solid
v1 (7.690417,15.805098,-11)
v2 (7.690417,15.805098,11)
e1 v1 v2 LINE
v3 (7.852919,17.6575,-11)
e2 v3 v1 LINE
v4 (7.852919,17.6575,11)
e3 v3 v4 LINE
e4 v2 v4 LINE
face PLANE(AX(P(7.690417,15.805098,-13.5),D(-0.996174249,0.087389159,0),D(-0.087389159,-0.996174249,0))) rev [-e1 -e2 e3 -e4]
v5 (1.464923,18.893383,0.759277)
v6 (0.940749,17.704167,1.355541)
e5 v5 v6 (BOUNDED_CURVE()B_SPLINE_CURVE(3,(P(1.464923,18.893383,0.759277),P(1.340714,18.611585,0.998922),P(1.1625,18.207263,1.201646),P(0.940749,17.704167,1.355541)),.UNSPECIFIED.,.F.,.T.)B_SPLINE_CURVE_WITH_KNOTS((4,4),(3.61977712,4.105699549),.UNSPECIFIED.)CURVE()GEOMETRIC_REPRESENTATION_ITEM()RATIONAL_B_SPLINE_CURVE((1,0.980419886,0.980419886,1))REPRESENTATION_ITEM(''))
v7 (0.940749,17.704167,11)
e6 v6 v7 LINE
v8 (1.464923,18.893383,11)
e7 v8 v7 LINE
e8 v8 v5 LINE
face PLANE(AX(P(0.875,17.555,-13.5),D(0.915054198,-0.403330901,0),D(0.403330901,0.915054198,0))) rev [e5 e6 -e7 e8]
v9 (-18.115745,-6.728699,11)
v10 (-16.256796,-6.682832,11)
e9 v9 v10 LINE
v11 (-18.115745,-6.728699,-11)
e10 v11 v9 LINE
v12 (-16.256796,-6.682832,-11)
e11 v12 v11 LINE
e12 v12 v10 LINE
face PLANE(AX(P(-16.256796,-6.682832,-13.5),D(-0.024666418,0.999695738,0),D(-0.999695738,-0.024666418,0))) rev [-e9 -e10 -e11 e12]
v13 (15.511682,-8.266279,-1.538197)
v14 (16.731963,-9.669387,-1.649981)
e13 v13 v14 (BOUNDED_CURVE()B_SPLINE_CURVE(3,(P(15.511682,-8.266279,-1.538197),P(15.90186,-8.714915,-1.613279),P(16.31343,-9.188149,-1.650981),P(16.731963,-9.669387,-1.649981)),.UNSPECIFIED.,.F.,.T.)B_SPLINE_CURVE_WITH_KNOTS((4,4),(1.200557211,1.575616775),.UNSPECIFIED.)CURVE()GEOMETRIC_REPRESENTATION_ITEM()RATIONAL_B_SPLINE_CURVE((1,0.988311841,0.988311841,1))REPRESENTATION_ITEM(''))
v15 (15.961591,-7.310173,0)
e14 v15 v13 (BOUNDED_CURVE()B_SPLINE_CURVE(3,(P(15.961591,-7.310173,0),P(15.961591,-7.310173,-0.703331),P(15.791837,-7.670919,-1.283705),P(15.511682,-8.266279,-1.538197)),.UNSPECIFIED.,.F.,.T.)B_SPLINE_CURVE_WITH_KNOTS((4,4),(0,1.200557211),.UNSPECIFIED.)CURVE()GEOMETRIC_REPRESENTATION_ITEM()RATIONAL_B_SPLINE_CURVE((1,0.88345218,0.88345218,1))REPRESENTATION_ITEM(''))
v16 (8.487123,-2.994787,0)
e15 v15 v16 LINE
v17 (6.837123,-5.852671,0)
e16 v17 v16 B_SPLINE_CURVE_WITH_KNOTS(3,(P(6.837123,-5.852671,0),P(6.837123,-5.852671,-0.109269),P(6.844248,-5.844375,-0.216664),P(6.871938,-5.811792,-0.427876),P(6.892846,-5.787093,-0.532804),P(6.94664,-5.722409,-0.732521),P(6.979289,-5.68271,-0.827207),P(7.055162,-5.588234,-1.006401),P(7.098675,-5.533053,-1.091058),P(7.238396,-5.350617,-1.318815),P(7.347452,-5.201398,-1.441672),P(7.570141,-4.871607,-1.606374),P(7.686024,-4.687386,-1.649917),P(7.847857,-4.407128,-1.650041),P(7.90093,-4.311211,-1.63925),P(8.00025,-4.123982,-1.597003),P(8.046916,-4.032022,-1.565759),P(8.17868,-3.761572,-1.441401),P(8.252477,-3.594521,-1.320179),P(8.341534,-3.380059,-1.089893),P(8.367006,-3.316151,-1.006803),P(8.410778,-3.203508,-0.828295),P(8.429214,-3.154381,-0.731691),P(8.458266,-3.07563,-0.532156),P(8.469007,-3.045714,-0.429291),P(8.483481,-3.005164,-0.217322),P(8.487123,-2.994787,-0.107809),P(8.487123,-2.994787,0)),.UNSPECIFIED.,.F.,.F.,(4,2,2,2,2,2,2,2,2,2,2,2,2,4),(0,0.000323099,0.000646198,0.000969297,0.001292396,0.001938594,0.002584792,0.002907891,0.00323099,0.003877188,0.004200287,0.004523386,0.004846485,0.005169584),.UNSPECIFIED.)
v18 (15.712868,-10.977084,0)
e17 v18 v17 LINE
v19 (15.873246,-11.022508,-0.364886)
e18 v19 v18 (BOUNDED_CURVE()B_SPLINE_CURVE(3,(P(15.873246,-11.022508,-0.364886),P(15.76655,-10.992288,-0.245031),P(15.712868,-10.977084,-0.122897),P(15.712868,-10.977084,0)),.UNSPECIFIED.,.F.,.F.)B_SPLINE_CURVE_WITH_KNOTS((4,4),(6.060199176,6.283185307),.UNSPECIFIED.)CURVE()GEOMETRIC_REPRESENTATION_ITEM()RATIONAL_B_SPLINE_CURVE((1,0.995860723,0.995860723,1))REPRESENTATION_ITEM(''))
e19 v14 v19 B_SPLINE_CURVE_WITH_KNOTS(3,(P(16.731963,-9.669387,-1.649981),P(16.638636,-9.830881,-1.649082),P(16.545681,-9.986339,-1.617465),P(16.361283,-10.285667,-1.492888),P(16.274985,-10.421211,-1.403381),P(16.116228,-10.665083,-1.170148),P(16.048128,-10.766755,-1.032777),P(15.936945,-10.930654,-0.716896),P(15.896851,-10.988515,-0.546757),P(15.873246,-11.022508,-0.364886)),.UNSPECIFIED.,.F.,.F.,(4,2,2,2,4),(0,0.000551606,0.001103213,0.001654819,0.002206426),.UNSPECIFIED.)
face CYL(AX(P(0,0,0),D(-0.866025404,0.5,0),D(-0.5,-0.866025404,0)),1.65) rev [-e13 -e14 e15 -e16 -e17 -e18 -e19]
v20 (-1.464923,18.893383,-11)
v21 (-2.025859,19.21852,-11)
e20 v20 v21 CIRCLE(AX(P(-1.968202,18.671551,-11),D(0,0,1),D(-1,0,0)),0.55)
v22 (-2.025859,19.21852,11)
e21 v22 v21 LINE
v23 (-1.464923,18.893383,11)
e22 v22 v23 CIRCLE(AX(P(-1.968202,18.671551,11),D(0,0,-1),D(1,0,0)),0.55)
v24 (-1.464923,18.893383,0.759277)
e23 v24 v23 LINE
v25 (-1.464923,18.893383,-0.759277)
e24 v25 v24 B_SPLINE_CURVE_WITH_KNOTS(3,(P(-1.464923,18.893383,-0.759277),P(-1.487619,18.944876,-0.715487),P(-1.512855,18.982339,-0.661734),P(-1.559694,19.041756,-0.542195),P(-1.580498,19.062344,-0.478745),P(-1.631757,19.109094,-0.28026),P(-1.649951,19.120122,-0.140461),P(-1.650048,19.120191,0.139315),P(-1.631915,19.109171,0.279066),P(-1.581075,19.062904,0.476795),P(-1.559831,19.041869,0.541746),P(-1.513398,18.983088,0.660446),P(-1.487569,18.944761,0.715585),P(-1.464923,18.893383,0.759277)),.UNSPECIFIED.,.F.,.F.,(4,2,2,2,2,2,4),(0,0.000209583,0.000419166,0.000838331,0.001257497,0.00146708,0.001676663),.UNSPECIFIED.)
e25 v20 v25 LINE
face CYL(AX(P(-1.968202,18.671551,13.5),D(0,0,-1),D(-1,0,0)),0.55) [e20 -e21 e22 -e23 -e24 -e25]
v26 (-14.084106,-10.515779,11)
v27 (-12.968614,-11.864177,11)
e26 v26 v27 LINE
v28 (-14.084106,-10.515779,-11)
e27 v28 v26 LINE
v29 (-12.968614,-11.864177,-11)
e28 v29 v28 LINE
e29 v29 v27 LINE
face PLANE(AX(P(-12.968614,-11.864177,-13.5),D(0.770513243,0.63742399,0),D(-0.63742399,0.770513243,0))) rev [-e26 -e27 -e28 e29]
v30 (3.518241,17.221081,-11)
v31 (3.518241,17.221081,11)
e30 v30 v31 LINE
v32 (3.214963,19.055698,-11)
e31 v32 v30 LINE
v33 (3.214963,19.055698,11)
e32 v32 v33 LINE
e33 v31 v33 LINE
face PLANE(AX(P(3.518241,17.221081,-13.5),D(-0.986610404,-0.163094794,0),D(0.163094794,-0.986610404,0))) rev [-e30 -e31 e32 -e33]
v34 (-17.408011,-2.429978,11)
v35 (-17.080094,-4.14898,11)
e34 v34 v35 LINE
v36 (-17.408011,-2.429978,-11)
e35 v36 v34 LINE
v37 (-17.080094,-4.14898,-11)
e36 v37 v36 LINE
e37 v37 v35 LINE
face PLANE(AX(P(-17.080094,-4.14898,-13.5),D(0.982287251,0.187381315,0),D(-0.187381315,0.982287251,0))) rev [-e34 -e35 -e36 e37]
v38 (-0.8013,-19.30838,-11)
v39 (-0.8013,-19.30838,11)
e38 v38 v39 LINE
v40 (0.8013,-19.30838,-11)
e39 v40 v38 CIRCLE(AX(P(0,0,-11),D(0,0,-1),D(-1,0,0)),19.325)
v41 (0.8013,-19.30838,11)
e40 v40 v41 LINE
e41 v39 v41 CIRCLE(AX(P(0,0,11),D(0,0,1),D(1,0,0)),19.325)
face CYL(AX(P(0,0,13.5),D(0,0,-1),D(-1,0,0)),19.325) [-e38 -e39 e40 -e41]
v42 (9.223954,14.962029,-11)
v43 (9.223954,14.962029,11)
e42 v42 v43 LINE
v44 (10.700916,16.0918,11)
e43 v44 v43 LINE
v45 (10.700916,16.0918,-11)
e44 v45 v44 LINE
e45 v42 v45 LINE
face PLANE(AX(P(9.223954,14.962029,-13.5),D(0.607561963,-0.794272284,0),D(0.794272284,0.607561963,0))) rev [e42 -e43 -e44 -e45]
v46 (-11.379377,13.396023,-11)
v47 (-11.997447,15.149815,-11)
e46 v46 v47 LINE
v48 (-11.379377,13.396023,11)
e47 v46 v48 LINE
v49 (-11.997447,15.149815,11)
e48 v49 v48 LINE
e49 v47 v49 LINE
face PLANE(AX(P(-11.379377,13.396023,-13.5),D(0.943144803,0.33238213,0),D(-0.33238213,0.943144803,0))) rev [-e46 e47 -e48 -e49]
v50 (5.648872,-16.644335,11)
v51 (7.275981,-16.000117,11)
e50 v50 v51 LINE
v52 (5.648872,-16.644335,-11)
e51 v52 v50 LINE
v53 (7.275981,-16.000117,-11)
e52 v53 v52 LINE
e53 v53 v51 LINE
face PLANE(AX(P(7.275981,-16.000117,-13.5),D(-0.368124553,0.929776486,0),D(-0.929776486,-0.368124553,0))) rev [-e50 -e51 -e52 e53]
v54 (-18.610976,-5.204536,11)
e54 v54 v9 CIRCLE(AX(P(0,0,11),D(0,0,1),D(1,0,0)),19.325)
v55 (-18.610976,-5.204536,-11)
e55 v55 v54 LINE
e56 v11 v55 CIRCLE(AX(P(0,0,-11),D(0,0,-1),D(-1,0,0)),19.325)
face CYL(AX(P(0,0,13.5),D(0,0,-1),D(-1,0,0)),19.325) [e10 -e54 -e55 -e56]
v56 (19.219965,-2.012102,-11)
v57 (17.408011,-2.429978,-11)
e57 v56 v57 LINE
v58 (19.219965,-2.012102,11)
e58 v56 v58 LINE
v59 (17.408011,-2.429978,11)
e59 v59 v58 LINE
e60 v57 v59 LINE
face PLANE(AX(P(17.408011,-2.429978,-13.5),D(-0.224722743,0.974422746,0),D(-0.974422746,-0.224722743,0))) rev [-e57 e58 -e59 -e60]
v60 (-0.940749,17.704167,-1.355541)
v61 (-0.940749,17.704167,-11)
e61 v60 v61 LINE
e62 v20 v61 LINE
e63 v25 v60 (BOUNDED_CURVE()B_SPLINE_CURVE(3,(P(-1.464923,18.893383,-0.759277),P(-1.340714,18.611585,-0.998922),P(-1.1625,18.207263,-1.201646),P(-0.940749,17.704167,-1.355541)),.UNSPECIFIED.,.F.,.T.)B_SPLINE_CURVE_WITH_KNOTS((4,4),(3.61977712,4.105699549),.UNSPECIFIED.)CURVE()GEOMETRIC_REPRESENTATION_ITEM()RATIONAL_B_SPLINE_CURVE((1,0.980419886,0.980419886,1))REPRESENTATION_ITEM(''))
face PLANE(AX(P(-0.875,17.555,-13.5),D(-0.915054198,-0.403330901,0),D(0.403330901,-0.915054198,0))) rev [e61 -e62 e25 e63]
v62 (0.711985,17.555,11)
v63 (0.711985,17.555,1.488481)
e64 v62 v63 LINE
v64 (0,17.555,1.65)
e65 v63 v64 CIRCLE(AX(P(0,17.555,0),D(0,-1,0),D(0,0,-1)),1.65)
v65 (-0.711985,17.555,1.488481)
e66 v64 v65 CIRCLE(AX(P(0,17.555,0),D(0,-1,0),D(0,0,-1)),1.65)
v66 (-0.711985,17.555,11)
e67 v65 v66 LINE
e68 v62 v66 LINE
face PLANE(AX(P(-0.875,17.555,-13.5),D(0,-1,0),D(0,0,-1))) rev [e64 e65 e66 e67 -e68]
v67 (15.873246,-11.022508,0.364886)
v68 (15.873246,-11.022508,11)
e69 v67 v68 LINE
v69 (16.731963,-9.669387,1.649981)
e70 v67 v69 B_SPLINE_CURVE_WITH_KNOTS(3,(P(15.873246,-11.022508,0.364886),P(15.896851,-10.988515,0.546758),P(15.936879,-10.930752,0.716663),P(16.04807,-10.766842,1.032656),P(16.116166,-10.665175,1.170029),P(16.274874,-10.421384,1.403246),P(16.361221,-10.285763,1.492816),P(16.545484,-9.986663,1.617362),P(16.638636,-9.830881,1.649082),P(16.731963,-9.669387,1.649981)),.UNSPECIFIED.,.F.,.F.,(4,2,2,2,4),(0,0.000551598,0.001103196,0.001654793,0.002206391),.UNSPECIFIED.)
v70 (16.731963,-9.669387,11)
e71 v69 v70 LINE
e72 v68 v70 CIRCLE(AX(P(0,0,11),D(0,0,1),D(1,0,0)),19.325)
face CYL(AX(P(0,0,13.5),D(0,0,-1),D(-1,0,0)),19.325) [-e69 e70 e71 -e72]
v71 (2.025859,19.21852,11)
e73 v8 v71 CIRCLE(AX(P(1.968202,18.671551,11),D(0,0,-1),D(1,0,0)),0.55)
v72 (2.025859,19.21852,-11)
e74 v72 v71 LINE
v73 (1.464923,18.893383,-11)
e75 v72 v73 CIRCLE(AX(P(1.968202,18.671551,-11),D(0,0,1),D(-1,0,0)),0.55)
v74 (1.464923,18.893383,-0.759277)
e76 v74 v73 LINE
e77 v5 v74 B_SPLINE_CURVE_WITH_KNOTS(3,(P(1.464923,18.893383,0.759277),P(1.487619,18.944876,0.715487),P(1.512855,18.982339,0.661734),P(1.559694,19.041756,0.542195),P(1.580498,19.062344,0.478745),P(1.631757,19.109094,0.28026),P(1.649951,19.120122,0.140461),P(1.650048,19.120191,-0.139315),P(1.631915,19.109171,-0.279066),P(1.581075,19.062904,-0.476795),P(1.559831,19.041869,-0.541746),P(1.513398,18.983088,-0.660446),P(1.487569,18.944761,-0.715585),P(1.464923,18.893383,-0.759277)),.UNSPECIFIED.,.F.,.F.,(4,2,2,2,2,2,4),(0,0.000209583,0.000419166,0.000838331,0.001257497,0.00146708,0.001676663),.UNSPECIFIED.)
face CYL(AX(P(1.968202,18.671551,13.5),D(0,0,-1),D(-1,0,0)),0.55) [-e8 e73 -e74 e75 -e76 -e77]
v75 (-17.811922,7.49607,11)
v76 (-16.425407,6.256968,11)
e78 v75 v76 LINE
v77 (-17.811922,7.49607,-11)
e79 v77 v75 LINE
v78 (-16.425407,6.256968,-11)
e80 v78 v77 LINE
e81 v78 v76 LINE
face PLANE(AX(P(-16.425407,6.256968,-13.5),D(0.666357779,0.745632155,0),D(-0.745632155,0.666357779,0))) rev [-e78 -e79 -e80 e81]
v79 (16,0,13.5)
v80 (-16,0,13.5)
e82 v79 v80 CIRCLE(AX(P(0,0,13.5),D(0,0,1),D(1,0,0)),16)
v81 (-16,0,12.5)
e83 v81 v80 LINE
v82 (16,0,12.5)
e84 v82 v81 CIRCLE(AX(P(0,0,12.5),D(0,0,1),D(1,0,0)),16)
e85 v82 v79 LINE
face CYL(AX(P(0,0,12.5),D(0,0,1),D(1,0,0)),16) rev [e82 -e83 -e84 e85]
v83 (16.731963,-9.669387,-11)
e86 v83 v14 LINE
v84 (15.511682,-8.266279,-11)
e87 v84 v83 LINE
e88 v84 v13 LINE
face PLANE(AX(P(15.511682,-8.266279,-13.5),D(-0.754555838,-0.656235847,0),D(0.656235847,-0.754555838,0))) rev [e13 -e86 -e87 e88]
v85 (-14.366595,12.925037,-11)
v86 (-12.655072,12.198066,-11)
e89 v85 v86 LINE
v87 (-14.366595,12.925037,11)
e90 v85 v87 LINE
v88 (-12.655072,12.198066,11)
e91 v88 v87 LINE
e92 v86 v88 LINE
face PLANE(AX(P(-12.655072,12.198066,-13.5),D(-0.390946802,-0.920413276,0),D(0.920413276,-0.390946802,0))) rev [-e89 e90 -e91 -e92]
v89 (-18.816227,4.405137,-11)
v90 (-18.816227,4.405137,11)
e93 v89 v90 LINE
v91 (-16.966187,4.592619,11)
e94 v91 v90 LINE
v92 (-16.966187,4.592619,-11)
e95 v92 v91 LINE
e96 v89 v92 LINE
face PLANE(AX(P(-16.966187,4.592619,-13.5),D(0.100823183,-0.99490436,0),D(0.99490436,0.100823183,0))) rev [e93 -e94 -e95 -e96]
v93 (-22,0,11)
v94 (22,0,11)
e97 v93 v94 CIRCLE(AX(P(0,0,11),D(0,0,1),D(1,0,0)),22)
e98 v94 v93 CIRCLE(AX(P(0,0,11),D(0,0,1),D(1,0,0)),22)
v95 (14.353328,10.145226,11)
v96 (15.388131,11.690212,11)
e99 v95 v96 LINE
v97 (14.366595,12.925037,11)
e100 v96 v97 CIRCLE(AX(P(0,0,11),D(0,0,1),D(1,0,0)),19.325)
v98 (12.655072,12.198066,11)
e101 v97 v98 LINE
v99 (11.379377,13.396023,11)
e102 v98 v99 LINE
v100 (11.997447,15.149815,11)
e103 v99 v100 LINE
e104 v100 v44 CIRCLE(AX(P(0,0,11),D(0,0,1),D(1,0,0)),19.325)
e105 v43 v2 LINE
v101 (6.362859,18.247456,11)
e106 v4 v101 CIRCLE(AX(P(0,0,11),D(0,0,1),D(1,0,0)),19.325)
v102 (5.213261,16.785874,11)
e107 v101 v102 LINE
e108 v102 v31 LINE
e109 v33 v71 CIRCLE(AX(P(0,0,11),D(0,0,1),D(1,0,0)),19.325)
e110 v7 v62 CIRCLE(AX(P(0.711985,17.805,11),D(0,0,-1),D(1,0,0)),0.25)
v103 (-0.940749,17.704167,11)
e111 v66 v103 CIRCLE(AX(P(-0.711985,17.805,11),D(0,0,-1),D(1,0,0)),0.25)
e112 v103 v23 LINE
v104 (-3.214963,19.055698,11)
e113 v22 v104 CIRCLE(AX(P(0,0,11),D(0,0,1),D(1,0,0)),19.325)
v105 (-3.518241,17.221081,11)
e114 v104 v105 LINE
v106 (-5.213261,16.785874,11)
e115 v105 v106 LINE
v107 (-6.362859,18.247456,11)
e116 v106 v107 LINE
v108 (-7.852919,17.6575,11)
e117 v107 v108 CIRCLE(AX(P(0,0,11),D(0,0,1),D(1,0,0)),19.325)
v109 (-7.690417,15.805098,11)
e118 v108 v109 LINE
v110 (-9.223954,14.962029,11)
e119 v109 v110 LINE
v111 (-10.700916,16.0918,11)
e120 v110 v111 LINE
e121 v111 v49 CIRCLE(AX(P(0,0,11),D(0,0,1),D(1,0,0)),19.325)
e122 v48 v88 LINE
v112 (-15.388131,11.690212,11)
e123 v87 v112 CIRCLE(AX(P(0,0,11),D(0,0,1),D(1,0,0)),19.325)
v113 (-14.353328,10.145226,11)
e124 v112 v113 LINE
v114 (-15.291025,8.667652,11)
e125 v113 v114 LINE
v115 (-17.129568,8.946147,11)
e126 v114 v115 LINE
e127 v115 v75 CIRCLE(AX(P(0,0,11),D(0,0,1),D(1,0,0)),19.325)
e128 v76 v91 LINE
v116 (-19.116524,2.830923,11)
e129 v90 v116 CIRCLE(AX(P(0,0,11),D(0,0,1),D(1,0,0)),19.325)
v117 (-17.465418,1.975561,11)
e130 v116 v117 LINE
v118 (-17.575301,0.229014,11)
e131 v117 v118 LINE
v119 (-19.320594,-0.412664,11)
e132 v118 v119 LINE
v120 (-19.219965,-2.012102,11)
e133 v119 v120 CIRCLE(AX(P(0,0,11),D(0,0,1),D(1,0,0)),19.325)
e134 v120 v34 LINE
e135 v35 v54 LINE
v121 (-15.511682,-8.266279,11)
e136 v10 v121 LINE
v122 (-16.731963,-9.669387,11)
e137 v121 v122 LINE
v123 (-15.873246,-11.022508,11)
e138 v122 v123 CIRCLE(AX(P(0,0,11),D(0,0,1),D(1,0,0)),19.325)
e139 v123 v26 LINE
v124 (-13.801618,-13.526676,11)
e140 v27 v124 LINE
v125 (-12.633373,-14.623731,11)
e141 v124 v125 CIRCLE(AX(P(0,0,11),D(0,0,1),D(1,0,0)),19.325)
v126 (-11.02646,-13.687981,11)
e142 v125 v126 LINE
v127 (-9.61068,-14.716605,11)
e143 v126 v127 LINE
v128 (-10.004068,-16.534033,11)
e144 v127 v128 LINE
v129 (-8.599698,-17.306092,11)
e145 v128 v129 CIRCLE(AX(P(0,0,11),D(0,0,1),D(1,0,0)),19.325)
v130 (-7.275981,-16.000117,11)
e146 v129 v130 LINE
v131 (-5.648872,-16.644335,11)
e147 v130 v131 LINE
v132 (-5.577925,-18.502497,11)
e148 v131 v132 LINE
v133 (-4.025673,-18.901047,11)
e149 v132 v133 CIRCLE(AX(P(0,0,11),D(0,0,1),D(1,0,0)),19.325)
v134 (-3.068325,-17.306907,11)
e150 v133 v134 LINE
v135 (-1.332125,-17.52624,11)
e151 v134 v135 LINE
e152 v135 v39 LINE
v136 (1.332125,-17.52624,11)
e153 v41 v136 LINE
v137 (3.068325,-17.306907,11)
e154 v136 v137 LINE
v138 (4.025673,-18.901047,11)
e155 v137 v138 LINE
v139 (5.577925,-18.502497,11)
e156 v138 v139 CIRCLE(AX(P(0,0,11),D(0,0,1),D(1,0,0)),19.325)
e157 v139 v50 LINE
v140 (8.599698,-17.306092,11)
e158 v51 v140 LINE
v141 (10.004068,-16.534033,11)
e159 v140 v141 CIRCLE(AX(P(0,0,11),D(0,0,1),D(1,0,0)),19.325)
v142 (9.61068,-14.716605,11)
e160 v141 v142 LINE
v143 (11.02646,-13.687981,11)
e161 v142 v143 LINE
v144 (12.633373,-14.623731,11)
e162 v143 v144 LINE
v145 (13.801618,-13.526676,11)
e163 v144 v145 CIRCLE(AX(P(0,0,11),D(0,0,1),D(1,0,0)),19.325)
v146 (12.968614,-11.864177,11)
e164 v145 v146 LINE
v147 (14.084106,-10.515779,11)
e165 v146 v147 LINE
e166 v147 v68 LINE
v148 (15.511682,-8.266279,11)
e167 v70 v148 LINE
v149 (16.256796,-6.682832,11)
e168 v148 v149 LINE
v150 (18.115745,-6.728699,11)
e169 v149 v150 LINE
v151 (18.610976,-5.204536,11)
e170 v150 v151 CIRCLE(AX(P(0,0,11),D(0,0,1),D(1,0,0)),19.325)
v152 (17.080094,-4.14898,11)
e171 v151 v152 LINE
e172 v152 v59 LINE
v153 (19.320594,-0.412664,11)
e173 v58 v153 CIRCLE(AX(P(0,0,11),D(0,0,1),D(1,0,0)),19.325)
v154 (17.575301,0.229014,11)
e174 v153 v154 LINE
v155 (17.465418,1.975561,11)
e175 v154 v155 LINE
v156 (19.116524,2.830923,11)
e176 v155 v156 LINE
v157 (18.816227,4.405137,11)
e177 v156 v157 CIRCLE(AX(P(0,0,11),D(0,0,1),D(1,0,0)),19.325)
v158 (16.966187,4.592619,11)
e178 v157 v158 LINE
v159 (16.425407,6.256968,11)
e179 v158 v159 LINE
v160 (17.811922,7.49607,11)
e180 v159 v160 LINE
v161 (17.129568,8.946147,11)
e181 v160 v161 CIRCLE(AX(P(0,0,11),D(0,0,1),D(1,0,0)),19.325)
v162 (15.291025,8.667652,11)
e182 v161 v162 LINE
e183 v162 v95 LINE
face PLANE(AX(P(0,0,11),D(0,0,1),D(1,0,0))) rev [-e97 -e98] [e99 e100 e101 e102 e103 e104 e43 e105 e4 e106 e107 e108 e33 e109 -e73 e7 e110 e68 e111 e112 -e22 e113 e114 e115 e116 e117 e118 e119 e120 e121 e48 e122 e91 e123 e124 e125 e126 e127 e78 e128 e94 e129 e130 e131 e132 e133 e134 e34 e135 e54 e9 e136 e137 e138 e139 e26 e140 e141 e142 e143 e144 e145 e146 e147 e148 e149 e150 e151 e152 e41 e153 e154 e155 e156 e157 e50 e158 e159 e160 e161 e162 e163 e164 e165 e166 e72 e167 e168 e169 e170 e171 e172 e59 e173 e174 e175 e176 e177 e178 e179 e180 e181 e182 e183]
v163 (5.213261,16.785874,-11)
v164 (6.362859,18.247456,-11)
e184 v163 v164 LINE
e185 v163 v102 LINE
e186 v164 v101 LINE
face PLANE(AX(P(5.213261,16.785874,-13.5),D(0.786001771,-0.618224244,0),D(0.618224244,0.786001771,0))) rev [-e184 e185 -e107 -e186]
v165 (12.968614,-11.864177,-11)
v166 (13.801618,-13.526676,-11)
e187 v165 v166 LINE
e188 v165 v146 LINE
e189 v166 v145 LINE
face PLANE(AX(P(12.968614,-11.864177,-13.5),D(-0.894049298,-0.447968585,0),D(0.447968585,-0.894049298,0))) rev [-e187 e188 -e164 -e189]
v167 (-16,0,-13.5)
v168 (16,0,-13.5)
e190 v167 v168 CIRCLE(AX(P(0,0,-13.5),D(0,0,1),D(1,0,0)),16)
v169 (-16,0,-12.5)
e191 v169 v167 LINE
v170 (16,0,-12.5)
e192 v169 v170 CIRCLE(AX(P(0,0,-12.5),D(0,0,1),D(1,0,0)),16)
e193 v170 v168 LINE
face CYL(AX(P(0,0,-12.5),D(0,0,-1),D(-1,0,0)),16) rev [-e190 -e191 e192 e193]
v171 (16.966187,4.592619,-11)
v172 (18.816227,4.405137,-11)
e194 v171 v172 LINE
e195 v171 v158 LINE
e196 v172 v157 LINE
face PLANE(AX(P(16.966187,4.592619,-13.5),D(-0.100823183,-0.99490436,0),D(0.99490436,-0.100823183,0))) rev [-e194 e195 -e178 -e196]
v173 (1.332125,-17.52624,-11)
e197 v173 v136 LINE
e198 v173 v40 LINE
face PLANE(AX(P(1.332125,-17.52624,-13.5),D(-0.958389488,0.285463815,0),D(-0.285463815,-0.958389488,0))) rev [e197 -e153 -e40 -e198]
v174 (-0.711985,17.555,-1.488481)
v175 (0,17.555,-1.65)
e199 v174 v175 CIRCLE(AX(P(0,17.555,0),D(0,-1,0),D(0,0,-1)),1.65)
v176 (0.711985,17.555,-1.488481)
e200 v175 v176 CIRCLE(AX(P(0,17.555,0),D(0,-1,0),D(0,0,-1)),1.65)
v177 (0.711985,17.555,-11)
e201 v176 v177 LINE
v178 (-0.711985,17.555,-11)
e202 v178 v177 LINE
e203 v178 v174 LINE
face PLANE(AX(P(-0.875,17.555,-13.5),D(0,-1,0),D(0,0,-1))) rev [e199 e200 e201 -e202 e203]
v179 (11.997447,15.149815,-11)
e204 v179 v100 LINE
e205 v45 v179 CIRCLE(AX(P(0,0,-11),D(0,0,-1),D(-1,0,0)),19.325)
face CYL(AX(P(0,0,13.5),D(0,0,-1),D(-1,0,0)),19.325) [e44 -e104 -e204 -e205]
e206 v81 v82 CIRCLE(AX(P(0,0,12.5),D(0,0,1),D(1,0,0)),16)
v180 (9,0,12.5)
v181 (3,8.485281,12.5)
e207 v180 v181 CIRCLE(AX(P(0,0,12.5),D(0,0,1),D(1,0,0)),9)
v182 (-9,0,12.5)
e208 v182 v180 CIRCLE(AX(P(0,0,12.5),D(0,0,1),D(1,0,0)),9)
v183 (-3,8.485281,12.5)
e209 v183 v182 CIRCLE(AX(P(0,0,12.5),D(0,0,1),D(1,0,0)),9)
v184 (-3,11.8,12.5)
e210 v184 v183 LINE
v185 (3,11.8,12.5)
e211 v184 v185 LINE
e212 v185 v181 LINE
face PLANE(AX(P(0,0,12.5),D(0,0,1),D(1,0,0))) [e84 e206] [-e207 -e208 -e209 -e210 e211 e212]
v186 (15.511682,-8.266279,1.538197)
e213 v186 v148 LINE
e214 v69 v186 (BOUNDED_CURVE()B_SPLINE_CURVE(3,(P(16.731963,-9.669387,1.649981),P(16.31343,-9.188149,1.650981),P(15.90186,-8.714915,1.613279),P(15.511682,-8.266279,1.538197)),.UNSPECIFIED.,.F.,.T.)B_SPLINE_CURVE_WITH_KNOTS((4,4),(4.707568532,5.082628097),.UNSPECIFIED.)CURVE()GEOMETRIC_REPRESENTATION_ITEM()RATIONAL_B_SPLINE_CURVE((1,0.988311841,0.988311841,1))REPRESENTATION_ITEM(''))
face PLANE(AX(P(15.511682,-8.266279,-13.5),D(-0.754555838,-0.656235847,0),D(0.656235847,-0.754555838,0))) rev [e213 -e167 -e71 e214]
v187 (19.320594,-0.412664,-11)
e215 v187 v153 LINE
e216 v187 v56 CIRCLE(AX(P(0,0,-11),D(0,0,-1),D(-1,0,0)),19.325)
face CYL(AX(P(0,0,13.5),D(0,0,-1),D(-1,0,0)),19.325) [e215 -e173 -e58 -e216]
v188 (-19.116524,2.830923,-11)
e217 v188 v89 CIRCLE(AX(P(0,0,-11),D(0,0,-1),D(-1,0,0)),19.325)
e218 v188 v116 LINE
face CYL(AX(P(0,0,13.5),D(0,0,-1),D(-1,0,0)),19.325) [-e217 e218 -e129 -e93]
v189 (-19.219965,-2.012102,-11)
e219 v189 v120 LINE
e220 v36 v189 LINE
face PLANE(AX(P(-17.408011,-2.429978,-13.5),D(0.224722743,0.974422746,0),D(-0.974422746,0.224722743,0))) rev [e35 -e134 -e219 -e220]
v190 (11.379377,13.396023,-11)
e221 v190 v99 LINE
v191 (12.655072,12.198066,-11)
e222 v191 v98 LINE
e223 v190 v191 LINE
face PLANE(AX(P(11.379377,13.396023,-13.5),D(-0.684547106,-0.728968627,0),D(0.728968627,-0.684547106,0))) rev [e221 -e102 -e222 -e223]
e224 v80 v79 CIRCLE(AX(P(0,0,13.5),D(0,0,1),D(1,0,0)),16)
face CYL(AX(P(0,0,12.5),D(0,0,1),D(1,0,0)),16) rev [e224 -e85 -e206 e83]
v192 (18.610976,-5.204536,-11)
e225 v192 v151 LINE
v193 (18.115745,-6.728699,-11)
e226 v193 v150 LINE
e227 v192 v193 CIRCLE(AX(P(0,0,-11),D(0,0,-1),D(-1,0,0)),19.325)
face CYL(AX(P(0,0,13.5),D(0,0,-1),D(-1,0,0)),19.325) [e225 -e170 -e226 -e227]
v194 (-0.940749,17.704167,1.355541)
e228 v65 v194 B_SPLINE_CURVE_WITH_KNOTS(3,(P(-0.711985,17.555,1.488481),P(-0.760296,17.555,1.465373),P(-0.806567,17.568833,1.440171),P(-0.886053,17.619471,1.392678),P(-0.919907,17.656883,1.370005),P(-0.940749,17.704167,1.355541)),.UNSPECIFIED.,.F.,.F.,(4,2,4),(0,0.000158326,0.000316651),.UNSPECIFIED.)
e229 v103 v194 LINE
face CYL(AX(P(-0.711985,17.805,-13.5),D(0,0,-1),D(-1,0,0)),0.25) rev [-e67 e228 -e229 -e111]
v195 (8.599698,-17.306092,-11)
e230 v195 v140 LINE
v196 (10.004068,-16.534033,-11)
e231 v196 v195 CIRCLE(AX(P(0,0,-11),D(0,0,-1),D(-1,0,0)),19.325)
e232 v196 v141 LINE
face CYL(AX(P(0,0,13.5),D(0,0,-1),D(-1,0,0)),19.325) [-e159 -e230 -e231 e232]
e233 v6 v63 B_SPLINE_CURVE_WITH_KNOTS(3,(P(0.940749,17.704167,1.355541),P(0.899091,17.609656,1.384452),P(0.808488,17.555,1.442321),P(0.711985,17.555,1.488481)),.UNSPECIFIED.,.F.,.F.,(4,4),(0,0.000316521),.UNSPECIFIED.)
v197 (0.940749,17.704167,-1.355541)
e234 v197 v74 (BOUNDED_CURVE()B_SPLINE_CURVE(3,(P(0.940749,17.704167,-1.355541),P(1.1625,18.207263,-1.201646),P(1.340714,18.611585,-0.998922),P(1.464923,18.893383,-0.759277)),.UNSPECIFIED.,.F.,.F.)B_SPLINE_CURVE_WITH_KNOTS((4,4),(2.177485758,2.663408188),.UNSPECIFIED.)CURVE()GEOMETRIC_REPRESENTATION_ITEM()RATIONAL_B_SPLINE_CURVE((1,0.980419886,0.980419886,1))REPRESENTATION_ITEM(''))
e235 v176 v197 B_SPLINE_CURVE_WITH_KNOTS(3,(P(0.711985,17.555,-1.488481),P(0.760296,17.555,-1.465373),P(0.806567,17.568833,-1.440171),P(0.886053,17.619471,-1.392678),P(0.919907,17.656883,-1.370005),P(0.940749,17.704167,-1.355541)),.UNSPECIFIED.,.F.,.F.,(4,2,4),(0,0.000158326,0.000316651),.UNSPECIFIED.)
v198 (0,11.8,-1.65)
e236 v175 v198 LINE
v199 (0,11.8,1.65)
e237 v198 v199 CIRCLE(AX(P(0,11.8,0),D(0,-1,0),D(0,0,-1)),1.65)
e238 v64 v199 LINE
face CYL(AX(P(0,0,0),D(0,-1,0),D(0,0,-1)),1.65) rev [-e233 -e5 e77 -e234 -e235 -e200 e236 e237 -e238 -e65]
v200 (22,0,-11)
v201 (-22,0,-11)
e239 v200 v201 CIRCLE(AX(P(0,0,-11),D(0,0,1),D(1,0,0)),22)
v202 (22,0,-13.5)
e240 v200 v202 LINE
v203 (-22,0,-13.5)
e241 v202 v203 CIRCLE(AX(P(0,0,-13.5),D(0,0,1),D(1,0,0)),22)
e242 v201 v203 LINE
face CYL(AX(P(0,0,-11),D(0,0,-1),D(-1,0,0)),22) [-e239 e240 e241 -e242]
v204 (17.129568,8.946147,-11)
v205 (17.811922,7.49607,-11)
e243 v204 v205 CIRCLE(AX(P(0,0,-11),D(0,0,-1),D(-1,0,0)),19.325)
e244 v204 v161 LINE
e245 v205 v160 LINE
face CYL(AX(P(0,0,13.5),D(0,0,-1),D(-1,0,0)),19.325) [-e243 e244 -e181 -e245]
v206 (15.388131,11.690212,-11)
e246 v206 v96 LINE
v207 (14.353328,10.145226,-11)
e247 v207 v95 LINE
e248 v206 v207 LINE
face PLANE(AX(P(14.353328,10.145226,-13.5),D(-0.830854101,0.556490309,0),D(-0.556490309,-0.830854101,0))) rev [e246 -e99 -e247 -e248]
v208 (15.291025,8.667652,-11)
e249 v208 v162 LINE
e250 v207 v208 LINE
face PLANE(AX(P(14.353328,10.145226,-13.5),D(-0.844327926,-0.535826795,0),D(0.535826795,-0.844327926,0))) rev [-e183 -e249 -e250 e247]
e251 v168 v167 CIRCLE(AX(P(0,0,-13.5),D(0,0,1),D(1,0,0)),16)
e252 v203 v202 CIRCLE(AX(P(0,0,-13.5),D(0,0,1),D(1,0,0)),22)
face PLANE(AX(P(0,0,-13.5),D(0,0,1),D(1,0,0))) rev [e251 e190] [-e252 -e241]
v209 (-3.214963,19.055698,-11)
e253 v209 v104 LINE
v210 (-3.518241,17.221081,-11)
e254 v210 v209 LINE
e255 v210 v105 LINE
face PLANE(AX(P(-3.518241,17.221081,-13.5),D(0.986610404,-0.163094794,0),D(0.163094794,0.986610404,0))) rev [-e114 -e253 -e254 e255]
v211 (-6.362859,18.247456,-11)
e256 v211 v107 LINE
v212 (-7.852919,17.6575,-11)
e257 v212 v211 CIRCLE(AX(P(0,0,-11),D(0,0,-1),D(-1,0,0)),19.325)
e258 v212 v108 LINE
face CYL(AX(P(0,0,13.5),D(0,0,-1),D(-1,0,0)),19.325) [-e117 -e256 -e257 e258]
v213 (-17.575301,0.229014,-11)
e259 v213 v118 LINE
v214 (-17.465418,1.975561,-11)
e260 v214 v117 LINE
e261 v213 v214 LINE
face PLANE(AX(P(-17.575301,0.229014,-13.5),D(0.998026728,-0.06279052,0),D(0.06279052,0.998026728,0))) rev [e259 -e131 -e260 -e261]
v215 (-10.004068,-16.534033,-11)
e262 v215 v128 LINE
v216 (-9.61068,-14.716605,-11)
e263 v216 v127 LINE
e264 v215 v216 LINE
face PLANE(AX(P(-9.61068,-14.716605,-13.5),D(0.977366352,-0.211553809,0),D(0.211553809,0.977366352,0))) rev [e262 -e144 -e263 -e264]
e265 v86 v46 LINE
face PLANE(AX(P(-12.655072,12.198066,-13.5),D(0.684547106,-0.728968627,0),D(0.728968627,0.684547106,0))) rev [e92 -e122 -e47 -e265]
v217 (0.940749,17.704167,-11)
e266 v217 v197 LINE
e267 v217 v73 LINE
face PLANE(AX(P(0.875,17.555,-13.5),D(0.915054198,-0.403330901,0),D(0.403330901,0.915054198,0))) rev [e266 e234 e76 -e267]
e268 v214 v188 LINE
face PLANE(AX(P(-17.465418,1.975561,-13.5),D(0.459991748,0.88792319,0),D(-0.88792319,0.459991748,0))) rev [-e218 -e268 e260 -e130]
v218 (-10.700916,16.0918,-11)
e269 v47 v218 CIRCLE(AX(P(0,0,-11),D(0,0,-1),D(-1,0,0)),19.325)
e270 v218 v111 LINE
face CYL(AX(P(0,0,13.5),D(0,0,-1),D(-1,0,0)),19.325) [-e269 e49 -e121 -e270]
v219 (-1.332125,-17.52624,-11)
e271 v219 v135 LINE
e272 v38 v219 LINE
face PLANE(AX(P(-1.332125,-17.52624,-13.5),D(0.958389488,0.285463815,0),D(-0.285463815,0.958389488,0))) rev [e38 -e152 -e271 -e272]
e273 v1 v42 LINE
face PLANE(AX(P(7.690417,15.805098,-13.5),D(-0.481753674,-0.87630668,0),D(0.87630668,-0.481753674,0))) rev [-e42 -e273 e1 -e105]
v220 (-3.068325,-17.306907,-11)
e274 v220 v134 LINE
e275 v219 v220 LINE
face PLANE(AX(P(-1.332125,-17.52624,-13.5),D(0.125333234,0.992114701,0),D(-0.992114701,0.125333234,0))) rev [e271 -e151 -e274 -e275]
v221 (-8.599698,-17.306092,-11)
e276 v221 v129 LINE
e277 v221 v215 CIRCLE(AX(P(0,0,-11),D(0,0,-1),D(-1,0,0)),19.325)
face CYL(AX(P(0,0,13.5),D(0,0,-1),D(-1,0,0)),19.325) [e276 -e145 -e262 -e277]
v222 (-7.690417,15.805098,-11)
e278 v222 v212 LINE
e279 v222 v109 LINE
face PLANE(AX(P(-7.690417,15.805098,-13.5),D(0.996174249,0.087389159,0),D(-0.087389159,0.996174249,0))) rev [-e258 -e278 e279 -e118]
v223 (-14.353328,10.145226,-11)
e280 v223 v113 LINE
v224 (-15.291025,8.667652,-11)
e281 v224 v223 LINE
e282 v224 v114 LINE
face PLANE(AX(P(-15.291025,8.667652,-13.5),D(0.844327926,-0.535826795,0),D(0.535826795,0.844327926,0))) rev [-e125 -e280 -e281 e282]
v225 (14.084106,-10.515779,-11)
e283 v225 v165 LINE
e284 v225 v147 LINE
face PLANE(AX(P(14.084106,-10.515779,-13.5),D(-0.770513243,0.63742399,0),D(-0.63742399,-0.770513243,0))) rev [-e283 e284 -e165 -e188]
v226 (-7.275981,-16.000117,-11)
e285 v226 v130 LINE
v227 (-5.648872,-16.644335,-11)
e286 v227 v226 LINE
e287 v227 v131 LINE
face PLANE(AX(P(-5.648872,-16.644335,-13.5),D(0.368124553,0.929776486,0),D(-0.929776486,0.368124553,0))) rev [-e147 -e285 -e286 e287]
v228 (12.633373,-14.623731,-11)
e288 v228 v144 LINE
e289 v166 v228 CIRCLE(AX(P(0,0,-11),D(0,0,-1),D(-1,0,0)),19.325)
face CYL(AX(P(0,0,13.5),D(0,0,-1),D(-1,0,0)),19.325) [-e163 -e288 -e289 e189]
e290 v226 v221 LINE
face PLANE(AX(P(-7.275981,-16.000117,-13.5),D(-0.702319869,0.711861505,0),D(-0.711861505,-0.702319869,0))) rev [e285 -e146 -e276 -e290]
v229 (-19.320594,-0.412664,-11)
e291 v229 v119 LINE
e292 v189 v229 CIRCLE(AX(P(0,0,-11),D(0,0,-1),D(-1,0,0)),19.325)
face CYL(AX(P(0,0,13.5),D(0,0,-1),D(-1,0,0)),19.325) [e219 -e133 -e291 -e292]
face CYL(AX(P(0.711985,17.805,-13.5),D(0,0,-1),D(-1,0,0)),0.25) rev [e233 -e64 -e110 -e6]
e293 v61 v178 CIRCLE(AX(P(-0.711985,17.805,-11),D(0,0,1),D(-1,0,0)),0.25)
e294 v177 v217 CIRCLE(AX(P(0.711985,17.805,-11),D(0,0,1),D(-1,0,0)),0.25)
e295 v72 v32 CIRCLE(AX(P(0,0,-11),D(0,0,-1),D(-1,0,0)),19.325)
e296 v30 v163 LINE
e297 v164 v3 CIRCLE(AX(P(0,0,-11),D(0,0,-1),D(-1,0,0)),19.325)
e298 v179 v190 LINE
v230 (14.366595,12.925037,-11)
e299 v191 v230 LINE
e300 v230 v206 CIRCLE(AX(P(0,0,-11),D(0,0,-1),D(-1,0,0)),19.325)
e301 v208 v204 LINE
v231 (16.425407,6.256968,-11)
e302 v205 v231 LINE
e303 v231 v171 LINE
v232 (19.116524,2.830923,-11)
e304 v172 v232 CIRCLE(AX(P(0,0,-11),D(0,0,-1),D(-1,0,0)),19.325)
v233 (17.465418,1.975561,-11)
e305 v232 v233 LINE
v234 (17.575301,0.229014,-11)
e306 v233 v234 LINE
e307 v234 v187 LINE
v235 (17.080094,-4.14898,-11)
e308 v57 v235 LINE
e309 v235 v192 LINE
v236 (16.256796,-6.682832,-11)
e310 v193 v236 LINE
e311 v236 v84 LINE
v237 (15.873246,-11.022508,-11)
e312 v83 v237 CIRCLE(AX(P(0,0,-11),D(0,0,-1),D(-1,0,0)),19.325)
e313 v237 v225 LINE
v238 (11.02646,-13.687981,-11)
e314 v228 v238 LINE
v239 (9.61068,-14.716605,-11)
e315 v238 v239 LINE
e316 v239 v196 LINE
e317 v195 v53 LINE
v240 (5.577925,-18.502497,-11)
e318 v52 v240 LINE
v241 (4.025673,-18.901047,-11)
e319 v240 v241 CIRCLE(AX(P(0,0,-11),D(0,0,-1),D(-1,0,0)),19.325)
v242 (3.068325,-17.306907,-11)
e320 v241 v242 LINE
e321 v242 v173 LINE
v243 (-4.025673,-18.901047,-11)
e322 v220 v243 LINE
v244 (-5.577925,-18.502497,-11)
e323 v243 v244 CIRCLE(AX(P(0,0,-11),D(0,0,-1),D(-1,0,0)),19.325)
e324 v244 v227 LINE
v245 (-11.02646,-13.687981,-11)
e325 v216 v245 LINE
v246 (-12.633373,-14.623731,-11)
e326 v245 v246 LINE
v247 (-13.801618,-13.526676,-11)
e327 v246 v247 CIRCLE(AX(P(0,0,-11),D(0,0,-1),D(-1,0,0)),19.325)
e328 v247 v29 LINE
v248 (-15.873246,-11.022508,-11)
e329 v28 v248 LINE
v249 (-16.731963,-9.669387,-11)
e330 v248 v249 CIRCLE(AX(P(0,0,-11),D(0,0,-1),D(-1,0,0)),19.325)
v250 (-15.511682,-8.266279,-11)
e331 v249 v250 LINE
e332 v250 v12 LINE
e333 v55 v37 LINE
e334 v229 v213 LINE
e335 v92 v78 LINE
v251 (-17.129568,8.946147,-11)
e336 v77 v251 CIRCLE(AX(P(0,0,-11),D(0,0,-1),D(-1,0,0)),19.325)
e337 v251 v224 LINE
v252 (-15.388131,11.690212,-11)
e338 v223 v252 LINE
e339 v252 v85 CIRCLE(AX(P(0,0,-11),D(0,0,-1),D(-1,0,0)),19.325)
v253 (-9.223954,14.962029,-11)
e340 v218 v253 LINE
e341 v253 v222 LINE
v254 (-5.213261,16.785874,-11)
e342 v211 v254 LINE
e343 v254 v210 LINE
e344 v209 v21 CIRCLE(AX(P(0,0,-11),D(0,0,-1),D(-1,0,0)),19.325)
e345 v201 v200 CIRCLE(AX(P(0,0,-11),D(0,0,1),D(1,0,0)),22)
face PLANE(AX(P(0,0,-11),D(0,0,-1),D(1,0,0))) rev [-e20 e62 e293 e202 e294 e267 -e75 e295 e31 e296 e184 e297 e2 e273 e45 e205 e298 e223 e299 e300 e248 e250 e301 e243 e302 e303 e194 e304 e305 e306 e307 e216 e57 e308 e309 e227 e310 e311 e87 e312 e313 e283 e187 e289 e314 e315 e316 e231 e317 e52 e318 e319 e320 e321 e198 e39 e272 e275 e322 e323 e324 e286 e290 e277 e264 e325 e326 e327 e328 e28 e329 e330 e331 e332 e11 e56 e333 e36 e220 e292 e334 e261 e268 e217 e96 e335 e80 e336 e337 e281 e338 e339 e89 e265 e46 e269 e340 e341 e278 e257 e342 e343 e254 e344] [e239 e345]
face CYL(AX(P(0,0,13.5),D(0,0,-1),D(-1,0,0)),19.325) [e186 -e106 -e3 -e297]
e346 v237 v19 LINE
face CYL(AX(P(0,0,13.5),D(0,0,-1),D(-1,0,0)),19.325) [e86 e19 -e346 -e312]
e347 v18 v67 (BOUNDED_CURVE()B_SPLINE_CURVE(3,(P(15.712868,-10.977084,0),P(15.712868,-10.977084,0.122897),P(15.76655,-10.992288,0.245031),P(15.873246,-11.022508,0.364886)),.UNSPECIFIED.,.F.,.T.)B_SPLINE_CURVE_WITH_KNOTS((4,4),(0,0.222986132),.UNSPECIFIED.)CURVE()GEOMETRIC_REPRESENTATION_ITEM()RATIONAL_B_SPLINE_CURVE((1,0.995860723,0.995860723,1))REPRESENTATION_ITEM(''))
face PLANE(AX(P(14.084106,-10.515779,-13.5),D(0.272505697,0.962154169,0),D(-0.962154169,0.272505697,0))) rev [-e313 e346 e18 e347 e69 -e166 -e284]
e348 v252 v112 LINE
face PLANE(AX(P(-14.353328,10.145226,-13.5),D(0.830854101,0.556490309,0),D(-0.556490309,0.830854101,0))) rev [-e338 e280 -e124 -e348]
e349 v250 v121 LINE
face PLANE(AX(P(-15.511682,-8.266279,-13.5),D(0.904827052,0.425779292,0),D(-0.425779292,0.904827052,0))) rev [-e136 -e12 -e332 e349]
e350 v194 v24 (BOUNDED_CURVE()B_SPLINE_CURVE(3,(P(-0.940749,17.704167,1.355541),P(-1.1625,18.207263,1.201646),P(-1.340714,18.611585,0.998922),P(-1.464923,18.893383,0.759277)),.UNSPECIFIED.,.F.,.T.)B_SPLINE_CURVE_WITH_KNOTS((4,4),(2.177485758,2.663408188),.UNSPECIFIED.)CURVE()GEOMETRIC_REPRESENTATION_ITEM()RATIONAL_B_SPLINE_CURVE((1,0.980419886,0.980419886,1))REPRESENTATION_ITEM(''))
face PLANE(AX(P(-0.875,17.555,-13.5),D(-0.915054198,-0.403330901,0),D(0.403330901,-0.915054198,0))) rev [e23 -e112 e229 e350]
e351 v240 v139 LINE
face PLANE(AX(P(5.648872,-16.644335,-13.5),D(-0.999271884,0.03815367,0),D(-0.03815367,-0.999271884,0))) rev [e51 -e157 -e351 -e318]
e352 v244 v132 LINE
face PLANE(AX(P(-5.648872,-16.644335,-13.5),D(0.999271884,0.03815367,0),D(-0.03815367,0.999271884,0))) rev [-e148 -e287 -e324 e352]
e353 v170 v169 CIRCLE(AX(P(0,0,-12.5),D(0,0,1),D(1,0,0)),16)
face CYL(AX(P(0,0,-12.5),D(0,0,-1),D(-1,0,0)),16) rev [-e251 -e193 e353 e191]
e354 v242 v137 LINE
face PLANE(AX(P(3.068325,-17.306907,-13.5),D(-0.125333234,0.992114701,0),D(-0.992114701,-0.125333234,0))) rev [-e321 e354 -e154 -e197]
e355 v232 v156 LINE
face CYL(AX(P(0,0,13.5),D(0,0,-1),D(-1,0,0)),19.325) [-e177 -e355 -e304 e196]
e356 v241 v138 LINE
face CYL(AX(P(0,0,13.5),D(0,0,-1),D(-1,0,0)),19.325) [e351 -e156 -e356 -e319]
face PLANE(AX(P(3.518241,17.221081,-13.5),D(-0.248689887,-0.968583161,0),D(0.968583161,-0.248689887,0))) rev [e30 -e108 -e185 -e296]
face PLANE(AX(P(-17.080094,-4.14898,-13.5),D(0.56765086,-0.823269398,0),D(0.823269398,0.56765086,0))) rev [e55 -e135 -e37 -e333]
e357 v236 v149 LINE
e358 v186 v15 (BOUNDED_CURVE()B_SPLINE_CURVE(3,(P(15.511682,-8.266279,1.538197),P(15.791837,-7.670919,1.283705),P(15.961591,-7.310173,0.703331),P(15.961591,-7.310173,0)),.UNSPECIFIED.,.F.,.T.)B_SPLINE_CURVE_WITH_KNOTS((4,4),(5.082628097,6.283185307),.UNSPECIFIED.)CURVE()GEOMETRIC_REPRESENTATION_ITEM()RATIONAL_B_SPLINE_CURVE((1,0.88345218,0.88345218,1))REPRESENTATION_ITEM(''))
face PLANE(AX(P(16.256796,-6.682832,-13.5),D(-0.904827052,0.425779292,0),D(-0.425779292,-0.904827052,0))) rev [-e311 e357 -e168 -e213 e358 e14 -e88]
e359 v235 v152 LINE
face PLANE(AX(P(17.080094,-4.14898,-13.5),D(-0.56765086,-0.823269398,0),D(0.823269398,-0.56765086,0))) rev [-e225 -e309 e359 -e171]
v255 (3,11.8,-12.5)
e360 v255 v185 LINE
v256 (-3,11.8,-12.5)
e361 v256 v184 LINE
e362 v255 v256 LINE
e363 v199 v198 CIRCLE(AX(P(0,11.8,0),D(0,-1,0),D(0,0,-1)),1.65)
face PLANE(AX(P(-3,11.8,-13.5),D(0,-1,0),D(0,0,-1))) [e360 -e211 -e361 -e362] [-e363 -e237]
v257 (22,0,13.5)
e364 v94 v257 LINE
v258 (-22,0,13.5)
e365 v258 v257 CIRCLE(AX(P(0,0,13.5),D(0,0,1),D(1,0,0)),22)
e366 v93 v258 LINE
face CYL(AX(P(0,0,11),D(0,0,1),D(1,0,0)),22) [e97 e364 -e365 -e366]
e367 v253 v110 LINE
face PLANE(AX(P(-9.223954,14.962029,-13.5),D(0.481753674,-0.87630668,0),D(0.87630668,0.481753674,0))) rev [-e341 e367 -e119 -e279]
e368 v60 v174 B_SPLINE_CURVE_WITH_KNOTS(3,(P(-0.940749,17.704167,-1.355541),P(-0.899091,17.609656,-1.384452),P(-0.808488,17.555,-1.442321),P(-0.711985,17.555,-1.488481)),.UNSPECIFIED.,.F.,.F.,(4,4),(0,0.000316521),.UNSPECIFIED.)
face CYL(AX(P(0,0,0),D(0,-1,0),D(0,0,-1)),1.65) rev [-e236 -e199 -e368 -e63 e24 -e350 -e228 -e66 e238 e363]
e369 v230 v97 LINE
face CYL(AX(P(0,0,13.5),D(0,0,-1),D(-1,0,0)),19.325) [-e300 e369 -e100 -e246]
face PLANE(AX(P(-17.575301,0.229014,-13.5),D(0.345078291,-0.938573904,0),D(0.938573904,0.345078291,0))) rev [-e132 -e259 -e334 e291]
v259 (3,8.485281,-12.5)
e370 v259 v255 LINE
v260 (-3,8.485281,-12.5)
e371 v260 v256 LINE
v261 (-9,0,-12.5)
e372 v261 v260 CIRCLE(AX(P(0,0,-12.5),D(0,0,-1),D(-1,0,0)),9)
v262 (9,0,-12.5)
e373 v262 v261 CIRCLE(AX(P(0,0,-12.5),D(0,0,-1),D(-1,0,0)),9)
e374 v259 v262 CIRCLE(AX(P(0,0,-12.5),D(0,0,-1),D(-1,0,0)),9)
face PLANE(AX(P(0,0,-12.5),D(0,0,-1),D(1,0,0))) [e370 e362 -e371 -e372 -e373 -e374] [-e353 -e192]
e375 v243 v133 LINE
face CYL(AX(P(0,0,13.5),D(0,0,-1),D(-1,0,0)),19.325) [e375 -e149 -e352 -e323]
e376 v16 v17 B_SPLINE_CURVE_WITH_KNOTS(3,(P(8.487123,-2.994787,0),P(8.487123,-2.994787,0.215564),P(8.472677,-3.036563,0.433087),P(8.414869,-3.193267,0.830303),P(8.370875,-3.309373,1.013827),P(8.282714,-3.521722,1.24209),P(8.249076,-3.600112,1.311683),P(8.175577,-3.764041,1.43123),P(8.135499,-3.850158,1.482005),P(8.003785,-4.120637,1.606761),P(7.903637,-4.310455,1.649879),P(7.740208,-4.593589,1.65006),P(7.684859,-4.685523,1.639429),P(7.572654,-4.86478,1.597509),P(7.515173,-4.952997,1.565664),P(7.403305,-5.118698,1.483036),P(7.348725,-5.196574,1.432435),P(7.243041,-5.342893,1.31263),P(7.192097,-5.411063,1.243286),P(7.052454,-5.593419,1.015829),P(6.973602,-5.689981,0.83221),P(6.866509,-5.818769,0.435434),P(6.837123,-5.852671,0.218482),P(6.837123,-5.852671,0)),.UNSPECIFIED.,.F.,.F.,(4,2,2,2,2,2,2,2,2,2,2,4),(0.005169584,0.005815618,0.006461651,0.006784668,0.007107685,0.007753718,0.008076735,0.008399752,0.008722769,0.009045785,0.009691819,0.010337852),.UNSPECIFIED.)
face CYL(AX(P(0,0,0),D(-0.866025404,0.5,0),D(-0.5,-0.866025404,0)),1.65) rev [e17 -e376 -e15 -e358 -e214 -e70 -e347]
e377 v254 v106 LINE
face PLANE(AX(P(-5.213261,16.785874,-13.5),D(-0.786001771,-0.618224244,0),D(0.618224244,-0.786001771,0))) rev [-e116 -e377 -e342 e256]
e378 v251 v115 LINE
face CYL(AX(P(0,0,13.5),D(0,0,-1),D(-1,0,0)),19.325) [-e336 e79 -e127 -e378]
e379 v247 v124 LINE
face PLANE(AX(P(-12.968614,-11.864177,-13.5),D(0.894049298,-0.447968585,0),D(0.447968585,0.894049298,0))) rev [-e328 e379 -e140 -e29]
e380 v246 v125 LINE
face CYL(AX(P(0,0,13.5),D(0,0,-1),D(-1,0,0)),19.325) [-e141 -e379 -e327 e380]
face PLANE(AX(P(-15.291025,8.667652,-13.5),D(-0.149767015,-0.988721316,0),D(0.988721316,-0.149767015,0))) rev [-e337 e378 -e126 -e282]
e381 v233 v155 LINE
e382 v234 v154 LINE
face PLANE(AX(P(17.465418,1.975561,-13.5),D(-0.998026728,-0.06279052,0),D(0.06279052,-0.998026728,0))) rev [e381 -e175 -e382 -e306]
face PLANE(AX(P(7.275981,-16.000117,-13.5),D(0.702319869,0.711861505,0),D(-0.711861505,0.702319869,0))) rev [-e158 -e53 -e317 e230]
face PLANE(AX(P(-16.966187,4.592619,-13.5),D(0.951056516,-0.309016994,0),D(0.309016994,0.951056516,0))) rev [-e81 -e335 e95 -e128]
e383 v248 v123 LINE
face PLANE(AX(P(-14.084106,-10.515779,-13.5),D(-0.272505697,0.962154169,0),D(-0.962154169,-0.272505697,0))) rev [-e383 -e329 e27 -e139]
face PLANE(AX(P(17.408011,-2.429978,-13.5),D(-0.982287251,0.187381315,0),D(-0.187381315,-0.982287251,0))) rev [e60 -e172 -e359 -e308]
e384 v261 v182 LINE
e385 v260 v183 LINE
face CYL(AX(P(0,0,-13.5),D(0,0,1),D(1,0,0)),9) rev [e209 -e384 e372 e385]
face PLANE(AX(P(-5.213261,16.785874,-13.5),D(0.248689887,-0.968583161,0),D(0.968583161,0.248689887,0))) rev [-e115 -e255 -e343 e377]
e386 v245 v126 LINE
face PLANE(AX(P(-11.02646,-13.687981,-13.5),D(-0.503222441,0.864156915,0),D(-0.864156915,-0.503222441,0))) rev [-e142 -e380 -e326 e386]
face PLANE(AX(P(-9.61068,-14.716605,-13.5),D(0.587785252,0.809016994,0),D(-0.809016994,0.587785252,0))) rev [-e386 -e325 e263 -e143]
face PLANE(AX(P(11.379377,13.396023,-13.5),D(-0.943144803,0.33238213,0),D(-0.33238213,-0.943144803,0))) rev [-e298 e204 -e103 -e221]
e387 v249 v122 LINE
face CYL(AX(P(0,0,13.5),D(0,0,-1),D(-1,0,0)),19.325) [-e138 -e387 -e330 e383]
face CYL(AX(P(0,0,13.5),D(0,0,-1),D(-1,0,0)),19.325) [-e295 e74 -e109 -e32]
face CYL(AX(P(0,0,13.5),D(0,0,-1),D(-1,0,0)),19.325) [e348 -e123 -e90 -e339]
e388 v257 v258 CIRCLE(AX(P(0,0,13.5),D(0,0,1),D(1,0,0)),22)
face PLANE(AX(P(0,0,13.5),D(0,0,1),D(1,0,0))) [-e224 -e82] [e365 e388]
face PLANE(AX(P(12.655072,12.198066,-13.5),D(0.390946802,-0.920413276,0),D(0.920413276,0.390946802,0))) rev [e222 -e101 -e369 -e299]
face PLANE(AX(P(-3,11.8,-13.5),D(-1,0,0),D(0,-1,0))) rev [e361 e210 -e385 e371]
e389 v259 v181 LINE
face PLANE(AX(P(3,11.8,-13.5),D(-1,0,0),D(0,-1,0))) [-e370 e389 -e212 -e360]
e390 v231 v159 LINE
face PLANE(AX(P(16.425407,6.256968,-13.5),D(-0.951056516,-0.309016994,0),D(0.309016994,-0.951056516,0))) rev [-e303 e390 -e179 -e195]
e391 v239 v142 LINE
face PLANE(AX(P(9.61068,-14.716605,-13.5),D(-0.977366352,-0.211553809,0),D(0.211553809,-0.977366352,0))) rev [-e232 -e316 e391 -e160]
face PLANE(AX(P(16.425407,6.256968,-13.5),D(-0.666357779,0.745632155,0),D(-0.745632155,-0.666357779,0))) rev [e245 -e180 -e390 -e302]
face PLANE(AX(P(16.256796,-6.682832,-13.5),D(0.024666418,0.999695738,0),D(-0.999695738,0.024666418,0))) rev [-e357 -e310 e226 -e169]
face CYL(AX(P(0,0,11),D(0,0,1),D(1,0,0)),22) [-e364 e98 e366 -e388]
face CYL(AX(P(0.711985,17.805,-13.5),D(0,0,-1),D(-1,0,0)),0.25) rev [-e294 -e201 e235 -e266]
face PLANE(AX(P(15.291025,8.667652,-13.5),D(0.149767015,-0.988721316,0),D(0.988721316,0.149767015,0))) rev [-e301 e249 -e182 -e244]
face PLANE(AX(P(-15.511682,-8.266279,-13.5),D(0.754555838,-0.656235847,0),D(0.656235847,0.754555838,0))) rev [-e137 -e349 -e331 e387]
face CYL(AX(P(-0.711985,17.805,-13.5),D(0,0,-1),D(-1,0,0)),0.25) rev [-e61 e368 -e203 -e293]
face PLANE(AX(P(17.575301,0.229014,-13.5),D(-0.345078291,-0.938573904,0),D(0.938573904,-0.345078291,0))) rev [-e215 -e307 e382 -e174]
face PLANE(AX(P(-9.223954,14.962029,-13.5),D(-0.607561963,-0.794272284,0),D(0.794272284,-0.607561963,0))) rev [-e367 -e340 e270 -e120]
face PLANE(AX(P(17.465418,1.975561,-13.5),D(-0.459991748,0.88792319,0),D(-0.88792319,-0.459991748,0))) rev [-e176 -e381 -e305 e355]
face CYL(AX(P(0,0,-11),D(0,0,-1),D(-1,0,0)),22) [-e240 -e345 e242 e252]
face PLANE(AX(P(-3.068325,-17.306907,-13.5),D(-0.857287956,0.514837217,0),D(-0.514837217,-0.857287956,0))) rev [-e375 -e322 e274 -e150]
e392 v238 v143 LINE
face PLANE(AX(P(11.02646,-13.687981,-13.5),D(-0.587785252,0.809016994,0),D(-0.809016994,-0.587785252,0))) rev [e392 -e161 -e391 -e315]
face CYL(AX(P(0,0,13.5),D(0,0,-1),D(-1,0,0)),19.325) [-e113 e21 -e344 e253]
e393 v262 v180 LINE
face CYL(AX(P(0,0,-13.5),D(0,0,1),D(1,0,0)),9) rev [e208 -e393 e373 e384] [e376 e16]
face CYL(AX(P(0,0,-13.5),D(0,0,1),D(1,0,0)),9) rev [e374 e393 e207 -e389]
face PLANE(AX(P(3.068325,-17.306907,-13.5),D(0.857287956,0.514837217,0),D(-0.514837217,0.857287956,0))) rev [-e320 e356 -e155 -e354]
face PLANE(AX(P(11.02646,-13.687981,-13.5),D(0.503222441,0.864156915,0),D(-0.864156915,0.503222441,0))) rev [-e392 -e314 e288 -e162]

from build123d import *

# Parameters (mm, degrees)
SKETCH_1_R               = 19.325
EXTRUDE_1_DEPTH          = 13.5
CUT_EXTRUDE_1_DEPTH      = 13.5
FILLET_3_R               = 0.55
FILLET_4_R               = 0.25
PATTERN_CIRCULAR_2_COUNT = 25
SKETCH_3_R               = 22
EXTRUDE_2_DEPTH          = 2.5
SKETCH_4_R               = 16
CUT_EXTRUDE_2_DEPTH      = 1
CUT_EXTRUDE_3_DEPTH      = 13.5
SKETCH_6_W               = 1.65
SKETCH_6_H               = 30.052558883
PATTERN_CIRCULAR_3_COUNT = 2
PATTERN_CIRCULAR_3_ANGLE = 120


with BuildPart() as part:
    # 草图1 → 凸台-拉伸1 (new, symmetric)
    with BuildSketch(Plane.XY):
        Circle(SKETCH_1_R)
    extrude(amount=EXTRUDE_1_DEPTH, both=True)

    # 草图2 → 切除-拉伸1 (cut, symmetric)
    with BuildSketch(Plane.XY):
        with BuildLine():
            Line((-0.875, 17.555), (0.875, 17.555))
            Line((0.875, 17.555), (1.625, 19.256557325))
            ThreePointArc((1.625, 19.256557325), (0, 19.325), (-1.625, 19.256557325))
            Line((-1.625, 19.256557325), (-0.875, 17.555))
        make_face()
    cut_extrude_1 = extrude(amount=CUT_EXTRUDE_1_DEPTH, both=True, mode=Mode.SUBTRACT)

    # 圆角3
    fillet_3_edges = [part.edges().sort_by_distance(p)[0] for p in [
        (-1.625, 19.256557325, 0),
        (1.625, 19.256557325, 0),
    ]]
    fillet(fillet_3_edges, radius=FILLET_3_R)

    # 圆角4
    fillet_4_edges = [part.edges().sort_by_distance(p)[0] for p in [
        (-0.875, 17.555, 0),
        (0.875, 17.555, 0),
    ]]
    fillet(fillet_4_edges, radius=FILLET_4_R)

    # 阵列(圆周)2: 切除-拉伸1 ×25 about axis
    pattern_circular_2_axis = Axis((0, 0, 0), (0, 0, 1))
    for i in range(1, PATTERN_CIRCULAR_2_COUNT):
        add(cut_extrude_1.rotate(pattern_circular_2_axis, i * 360 / PATTERN_CIRCULAR_2_COUNT), mode=Mode.SUBTRACT)

    # 草图3 → 凸台-拉伸2 (add)
    with BuildSketch(Plane.XY.offset(13.5)):
        Circle(SKETCH_3_R)
    extrude_2 = extrude(amount=-EXTRUDE_2_DEPTH)

    # 镜向1: 凸台-拉伸2 across plane
    add(extrude_2.mirror(Plane.XY))

    # 草图4 → 切除-拉伸2 (cut)
    with BuildSketch(Plane.XY.offset(13.5)):
        Circle(SKETCH_4_R)
    cut_extrude_2 = extrude(amount=-CUT_EXTRUDE_2_DEPTH, mode=Mode.SUBTRACT)

    # 镜向2: 切除-拉伸2 across plane
    add(cut_extrude_2.mirror(Plane.XY), mode=Mode.SUBTRACT)

    # 草图5 → 切除-拉伸3 (cut, symmetric)
    with BuildSketch(Plane.XY):
        with BuildLine():
            Line((-3, 11.8), (3, 11.8))
            Line((3, 11.8), (3, 8.485281374))
            ThreePointArc((3, 8.485281374), (0, -9), (-3, 8.485281374))
            Line((-3, 8.485281374), (-3, 11.8))
        make_face()
    extrude(amount=CUT_EXTRUDE_3_DEPTH, both=True, mode=Mode.SUBTRACT)

    # 草图6 → M4 螺纹孔1 (revolve, cut)
    with BuildSketch(Plane(origin=(0, 0, 0), x_dir=(0, 0, -1), z_dir=(1, 0, 0))):
        with Locations((0.825, 15.026279442)):
            Rectangle(SKETCH_6_W, SKETCH_6_H)
    hole_wizard_m4_1 = revolve(axis=Axis((0, -6.35, 0), (0, 1, 0)), mode=Mode.SUBTRACT)

    # 阵列(圆周)3: M4 螺纹孔1 ×2 about axis
    pattern_circular_3_axis = Axis((0, 0, 13.5), (0, 0, -1))
    for i in range(1, PATTERN_CIRCULAR_3_COUNT):
        add(hole_wizard_m4_1.rotate(pattern_circular_3_axis, i * PATTERN_CIRCULAR_3_ANGLE / (PATTERN_CIRCULAR_3_COUNT - 1)), mode=Mode.SUBTRACT)


solid = part.part
